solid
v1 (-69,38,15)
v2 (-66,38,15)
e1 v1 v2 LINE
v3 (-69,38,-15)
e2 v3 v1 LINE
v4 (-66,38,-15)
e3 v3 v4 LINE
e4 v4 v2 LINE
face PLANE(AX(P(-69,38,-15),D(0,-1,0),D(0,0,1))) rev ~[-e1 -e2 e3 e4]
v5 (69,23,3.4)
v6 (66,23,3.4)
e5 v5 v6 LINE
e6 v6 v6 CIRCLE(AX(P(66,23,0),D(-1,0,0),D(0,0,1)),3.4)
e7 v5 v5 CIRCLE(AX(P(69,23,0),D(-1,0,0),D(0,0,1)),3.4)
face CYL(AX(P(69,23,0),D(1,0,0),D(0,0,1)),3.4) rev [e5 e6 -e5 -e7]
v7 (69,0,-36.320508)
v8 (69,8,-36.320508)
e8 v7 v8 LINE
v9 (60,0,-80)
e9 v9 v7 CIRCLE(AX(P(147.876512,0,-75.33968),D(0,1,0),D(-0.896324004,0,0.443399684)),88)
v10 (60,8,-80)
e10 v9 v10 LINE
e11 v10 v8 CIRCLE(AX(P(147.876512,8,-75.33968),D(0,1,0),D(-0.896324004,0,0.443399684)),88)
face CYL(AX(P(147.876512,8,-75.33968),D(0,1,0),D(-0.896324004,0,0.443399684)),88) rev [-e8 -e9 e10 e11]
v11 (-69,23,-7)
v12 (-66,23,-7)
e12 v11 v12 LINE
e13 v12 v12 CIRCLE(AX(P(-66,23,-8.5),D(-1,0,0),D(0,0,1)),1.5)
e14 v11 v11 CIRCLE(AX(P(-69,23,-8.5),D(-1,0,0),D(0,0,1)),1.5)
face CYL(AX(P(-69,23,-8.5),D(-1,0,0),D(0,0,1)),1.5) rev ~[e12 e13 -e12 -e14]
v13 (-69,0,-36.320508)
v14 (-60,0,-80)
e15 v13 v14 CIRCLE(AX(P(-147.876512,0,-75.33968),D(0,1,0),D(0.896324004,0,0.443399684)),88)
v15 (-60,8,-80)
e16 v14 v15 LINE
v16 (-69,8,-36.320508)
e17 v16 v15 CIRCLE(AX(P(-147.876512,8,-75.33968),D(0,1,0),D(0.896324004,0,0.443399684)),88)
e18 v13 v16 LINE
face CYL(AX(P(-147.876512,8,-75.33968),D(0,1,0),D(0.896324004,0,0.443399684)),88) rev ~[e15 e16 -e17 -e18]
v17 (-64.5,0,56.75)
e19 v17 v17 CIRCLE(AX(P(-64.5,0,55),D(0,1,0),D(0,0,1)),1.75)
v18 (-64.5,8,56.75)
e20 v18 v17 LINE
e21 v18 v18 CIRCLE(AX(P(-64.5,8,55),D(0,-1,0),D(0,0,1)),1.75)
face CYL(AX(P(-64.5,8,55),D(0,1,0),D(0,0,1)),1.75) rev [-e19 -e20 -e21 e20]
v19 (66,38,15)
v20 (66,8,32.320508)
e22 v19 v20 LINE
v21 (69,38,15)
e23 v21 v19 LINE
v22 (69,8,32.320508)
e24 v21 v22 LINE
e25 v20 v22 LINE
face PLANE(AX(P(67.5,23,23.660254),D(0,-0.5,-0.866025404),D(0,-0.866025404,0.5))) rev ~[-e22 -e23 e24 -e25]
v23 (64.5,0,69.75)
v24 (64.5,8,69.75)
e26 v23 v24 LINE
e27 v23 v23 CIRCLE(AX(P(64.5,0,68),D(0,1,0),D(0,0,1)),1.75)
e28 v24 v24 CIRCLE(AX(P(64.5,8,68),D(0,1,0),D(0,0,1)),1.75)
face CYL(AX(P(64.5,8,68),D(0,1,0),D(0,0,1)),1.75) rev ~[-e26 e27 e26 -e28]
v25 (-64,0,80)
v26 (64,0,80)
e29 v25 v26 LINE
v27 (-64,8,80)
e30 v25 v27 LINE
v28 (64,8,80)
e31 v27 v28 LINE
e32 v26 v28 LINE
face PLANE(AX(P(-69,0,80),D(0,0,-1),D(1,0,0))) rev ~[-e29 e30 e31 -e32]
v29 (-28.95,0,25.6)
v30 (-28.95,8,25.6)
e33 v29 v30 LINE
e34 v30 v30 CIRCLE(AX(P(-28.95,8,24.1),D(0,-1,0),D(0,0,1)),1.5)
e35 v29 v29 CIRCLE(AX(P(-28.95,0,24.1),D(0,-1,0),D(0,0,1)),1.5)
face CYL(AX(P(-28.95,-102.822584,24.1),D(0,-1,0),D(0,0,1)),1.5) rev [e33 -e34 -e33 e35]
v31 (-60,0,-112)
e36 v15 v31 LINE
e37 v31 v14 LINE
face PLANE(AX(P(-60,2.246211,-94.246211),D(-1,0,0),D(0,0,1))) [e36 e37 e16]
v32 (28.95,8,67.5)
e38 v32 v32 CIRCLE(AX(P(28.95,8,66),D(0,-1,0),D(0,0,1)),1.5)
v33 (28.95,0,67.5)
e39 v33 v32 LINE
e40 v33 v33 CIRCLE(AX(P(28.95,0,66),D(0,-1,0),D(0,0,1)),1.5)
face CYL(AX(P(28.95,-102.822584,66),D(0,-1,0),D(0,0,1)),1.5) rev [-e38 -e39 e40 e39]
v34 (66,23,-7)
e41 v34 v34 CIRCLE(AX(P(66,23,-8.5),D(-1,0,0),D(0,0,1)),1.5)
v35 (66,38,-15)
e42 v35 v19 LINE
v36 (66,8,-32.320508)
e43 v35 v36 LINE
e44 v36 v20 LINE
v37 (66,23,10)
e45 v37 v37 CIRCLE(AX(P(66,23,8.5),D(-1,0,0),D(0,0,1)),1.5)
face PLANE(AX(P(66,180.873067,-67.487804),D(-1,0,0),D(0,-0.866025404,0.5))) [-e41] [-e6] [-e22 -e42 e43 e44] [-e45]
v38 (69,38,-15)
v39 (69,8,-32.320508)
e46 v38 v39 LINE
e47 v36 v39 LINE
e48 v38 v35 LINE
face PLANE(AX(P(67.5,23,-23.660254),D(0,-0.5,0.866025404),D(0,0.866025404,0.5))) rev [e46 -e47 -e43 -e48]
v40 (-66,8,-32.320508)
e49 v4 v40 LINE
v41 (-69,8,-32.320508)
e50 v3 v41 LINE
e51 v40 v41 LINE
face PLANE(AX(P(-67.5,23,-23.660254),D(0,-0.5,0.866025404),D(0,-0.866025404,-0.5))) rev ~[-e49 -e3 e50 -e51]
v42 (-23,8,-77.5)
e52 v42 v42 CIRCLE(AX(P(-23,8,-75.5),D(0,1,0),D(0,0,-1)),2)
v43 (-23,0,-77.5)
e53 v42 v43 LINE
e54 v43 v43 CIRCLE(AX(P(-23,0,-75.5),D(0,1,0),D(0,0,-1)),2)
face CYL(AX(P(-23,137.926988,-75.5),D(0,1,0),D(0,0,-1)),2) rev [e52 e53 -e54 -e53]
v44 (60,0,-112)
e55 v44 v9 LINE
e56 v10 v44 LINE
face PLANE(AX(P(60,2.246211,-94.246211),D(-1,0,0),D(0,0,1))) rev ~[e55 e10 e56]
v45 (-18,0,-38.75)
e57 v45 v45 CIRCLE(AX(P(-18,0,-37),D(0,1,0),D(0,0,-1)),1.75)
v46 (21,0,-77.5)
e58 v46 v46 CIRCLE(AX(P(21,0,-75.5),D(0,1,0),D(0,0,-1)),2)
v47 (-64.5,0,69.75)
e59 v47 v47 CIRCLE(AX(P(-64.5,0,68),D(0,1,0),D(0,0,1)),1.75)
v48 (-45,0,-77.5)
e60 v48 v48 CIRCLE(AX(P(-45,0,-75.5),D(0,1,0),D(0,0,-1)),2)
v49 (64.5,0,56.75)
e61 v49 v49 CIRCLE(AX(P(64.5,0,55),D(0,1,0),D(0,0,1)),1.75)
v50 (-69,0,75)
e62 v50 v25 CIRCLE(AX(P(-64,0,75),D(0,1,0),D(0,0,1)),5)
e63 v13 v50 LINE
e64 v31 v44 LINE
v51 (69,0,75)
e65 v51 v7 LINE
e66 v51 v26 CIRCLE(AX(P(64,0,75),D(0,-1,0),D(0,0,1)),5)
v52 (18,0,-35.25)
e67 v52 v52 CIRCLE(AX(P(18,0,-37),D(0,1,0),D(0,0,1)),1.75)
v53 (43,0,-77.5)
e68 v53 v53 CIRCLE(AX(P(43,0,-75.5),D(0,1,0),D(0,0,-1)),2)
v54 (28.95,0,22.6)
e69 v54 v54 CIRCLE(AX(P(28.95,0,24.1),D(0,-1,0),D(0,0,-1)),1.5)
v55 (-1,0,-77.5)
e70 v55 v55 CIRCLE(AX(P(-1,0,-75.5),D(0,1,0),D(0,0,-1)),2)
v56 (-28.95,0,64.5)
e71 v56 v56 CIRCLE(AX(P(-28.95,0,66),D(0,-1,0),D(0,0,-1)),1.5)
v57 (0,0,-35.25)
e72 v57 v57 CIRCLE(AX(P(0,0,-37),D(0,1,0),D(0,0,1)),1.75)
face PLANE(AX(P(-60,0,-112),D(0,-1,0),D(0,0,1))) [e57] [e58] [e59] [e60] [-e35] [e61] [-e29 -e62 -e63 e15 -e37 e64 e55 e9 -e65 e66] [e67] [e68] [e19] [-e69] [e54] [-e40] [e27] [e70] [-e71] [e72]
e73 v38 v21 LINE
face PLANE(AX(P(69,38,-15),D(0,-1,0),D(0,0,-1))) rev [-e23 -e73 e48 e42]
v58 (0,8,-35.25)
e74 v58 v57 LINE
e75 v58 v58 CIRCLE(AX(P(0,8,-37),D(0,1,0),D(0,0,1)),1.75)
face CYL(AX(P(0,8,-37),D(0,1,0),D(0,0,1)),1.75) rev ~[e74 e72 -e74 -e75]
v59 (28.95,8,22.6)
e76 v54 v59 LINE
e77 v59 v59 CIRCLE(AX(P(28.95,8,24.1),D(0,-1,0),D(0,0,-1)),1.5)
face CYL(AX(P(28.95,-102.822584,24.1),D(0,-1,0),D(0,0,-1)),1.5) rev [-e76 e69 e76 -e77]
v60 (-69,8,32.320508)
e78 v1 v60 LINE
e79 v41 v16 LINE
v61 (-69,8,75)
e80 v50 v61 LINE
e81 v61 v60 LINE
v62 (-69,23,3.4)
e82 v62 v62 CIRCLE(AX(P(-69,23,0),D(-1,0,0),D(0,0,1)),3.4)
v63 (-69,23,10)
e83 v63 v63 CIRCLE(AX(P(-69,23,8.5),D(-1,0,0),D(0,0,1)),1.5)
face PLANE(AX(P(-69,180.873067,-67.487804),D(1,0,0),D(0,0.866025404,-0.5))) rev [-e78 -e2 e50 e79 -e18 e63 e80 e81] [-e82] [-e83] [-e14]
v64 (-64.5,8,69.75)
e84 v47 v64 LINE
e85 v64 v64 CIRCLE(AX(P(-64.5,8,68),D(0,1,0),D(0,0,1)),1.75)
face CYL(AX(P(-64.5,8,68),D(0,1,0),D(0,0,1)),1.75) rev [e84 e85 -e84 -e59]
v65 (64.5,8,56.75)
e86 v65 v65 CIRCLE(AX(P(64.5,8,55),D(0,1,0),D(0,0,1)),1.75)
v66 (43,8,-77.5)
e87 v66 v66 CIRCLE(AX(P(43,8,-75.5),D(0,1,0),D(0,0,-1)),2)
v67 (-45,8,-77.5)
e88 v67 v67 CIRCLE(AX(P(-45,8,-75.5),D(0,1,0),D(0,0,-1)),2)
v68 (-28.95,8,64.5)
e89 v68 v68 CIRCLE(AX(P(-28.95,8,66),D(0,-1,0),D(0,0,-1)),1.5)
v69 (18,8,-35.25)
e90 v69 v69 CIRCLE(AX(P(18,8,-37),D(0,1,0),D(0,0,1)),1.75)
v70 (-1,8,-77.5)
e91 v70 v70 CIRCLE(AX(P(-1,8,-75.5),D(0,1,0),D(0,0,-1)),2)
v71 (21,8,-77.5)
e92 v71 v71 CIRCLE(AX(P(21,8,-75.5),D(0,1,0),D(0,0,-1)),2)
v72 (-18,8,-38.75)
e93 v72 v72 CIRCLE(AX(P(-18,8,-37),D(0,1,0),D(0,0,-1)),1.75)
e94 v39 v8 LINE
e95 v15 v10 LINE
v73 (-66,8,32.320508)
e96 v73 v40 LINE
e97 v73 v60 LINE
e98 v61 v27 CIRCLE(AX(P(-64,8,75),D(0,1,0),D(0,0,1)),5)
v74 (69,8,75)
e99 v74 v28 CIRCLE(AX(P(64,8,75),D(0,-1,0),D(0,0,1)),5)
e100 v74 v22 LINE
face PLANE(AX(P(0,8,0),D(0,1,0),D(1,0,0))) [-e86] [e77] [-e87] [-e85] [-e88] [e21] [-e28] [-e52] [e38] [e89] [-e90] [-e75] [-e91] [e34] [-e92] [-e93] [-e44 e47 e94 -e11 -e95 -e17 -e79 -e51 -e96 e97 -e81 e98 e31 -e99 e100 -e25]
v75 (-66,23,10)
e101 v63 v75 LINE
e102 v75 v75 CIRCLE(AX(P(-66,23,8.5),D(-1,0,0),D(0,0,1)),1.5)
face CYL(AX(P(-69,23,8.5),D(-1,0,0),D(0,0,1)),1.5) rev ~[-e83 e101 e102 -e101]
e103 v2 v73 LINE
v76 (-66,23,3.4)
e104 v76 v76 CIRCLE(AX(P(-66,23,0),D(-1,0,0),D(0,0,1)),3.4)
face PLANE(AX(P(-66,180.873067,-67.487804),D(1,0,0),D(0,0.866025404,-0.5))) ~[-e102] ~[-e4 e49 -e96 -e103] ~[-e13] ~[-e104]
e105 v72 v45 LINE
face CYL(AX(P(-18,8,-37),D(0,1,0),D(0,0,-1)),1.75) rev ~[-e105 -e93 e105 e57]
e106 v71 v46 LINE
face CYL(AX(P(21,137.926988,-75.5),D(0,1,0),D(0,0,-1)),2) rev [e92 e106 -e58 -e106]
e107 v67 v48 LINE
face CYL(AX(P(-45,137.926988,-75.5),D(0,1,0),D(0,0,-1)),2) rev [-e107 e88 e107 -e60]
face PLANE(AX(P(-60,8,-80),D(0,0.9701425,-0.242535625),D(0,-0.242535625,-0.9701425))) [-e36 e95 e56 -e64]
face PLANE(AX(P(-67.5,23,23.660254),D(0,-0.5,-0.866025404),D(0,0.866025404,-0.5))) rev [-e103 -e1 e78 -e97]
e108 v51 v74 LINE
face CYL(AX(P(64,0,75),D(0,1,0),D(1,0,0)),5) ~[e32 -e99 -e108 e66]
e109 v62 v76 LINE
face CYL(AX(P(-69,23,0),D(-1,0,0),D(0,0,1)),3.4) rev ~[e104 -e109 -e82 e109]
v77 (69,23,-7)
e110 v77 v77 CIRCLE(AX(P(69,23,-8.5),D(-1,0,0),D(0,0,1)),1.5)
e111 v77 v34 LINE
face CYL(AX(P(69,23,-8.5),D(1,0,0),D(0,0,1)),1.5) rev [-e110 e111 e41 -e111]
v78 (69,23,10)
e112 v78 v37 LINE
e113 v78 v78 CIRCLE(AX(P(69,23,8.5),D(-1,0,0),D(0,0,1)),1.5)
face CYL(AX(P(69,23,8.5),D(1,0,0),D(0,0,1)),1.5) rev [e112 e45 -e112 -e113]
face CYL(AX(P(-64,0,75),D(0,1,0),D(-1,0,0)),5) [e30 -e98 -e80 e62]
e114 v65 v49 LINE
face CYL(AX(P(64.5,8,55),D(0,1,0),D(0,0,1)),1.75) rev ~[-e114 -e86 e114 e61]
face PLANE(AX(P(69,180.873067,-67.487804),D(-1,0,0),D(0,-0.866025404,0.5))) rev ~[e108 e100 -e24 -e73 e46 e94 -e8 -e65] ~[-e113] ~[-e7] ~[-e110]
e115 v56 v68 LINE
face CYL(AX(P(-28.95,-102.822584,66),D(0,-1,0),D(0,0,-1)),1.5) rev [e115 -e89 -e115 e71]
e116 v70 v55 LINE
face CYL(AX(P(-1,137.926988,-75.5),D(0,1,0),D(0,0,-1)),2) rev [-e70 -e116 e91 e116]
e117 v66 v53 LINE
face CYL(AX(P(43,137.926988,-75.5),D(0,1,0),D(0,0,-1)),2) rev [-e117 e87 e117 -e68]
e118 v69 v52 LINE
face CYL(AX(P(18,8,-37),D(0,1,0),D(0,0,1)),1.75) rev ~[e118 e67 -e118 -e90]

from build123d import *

# Parameters (mm, degrees)
SKETCH1_W                = 138
SKETCH1_H                = 160
BOSS_EXTRUDE1_DEPTH      = 8
SKETCH9_W                = 30
SKETCH9_H                = 38
SKETCH9_R                = 3.4
SKETCH9_R_2              = 1.5
BOSS_EXTRUDE4_DEPTH      = 3
RIB2_REACH               = 165.976
SKETCH10_WALL_W          = 364.592232036
SKETCH10_WALL_H          = 3
MIRROR4_COPY_1_REACH     = 165.976
MIRROR4_COPY_1_SKETCH_W  = 364.592232036
MIRROR4_COPY_1_SKETCH_H  = 3
CUT_EXTRUDE2_DEPTH       = 110.822584198
CUT_EXTRUDE2_DEPTH_BACK  = 110.822584198
SKETCH11_R               = 1.5
FILLET1_R                = 5
SKETCH12_R               = 1.75
CUT_EXTRUDE3_DEPTH       = 110.822584198
CUT_EXTRUDE4_DEPTH       = 110.822584198
BOSS_EXTRUDE5_DEPTH      = 60
BOSS_EXTRUDE5_DEPTH_BACK = 60
CUT_EXTRUDE5_DEPTH       = 137.926987844
CUT_EXTRUDE5_DEPTH_BACK  = 137.926987844
SKETCH15_R               = 2
SKETCH16_R               = 1.75
CUT_EXTRUDE6_DEPTH       = 50


with BuildPart() as part:
    # Sketch1 → Boss-Extrude1 (new body)
    with BuildSketch(Plane(origin=(0, 0, 0), x_dir=(1, 0, 0), z_dir=(0, 1, 0))):
        Rectangle(SKETCH1_W, SKETCH1_H)
    extrude(amount=BOSS_EXTRUDE1_DEPTH)

    # Sketch9 → Boss-Extrude4 (add)
    with BuildSketch(Plane.ZY.offset(69)):
        with Locations((0, 19)):
            Rectangle(SKETCH9_W, SKETCH9_H)
        with Locations((0, 23)):
            Circle(SKETCH9_R, mode=Mode.SUBTRACT)
        with Locations((8.5, 23)):
            Circle(SKETCH9_R_2, mode=Mode.SUBTRACT)
        with Locations((-8.5, 23)):
            Circle(SKETCH9_R_2, mode=Mode.SUBTRACT)
    boss_extrude4 = extrude(amount=-BOSS_EXTRUDE4_DEPTH)

    # Sketch10 wall → Rib2 (add, up to next)
    with BuildSketch(Plane(origin=(-69, 23, -23.660254038), x_dir=(0, -0.866025403781, -0.500000000007), z_dir=(0, -0.500000000007, 0.866025403781)), mode=Mode.PRIVATE) as rib2_sk1:
        with Locations((0, 1.5)):
            Rectangle(SKETCH10_WALL_W, SKETCH10_WALL_H)
    rib2_tool1 = extrude(rib2_sk1.sketch, amount=RIB2_REACH, mode=Mode.PRIVATE) - part.part
    rib2 = rib2_tool1.solids().sort_by_distance((-69, 23, -23.660254038))[0]
    add(rib2)

    # Mirror3: Rib2 across plane
    add(rib2.mirror(Plane.XY))

    # Mirror4: Boss-Extrude4, Rib2 across plane
    add(boss_extrude4.mirror(Plane(origin=(0, 0, 0), x_dir=(0, 0, 1), z_dir=(1, 0, 0))))
    add(rib2.mirror(Plane(origin=(0, 0, 0), x_dir=(0, 0, 1), z_dir=(1, 0, 0))))

    # Mirror4 copy 1 sketch → Mirror4 copy 1 (add, up to next)
    with BuildSketch(Plane(origin=(69, 23, 23.660254038), x_dir=(0, -0.866025403781, 0.500000000007), z_dir=(0, -0.500000000007, -0.866025403781)), mode=Mode.PRIVATE) as mirror4_copy_1_sk1:
        with Locations((0, 1.5)):
            Rectangle(MIRROR4_COPY_1_SKETCH_W, MIRROR4_COPY_1_SKETCH_H)
    mirror4_copy_1_tool1 = extrude(mirror4_copy_1_sk1.sketch, amount=MIRROR4_COPY_1_REACH, mode=Mode.PRIVATE) - part.part
    add(mirror4_copy_1_tool1.solids().sort_by_distance((69, 23, 23.660254038))[0])

    # Sketch11 → Cut-Extrude2 (cut, two sides: drawn at the far end of the back side and taken through both)
    with BuildSketch(Plane(origin=(0, 8, 0), x_dir=(1, 0, 0), z_dir=(0, 1, 0)).offset(-CUT_EXTRUDE2_DEPTH_BACK)):
        with Locations(Location((-28.95, -24.1, 0), (0, 0, 270))):
            Circle(SKETCH11_R)
        with Locations(Location((28.95, -24.1, 0), (0, 0, 90))):
            Circle(SKETCH11_R)
        with Locations(Location((-28.95, -66, 0), (0, 0, 90))):
            Circle(SKETCH11_R)
        with Locations(Location((28.95, -66, 0), (0, 0, 270))):
            Circle(SKETCH11_R)
    extrude(amount=CUT_EXTRUDE2_DEPTH + CUT_EXTRUDE2_DEPTH_BACK, mode=Mode.SUBTRACT)

    # Fillet1
    fillet1_edges = [part.edges().sort_by_distance(p)[0] for p in [
        (69, 4, 80),
        (-69, 4, 80),
        (-69, 4, -80),
        (69, 4, -80),
    ]]
    fillet(fillet1_edges, radius=FILLET1_R)

    # Sketch12 → Cut-Extrude3 (cut, symmetric)
    with BuildSketch(Plane(origin=(0, 8, 0), x_dir=(1, 0, 0), z_dir=(0, 1, 0))):
        with Locations(Location((64.5, -55, 0), (0, 0, 270))):
            Circle(SKETCH12_R)
        with Locations(Location((64.5, -68, 0), (0, 0, 270))):
            Circle(SKETCH12_R)
    cut_extrude3 = extrude(amount=CUT_EXTRUDE3_DEPTH, both=True, mode=Mode.SUBTRACT)

    # Mirror5: Cut-Extrude3 across plane
    add(cut_extrude3.mirror(Plane(origin=(0, 0, 0), x_dir=(0, 0, 1), z_dir=(1, 0, 0))), mode=Mode.SUBTRACT)

    # Sketch13 → Cut-Extrude4 (cut, symmetric)
    with BuildSketch(Plane(origin=(0, 8, 0), x_dir=(1, 0, 0), z_dir=(0, 1, 0))):
        with BuildLine():
            Line((60, 80), (80.385419548, 90.585690096))
            Line((80.385419548, 90.585690096), (122.100847158, 60.329129947))
            Line((122.100847158, 60.329129947), (69, 36.320508076))
            ThreePointArc((69, 36.320508076), (61.687085415, 57.580663247), (60, 80))
        make_face()
    cut_extrude4 = extrude(amount=CUT_EXTRUDE4_DEPTH, both=True, mode=Mode.SUBTRACT)

    # Mirror6: Cut-Extrude4 across plane
    add(cut_extrude4.mirror(Plane(origin=(0, 0, 0), x_dir=(0, 0, 1), z_dir=(1, 0, 0))), mode=Mode.SUBTRACT)

    # Sketch14 → Boss-Extrude5 (add, two sides: drawn at the far end of the back side and taken through both)
    with BuildSketch(Plane(origin=(0, 0, 0), x_dir=(0, 0, -1), z_dir=(1, 0, 0)).offset(-BOSS_EXTRUDE5_DEPTH_BACK)):
        Polygon((80, 0), (80, 8), (112, 0), align=None)
    extrude(amount=BOSS_EXTRUDE5_DEPTH + BOSS_EXTRUDE5_DEPTH_BACK)

    # Sketch15 → Cut-Extrude5 (cut, two sides: drawn at the far end of the back side and taken through both)
    with BuildSketch(Plane.XZ.offset(-CUT_EXTRUDE5_DEPTH_BACK)):
        with Locations(Location((-45, -75.5, 0), (0, 0, 270))):
            Circle(SKETCH15_R)
        with Locations(Location((-23, -75.5, 0), (0, 0, 270))):
            Circle(SKETCH15_R)
        with Locations(Location((-1, -75.5, 0), (0, 0, 270))):
            Circle(SKETCH15_R)
        with Locations(Location((21, -75.5, 0), (0, 0, 270))):
            Circle(SKETCH15_R)
        with Locations(Location((43, -75.5, 0), (0, 0, 270))):
            Circle(SKETCH15_R)
    extrude(amount=CUT_EXTRUDE5_DEPTH + CUT_EXTRUDE5_DEPTH_BACK, mode=Mode.SUBTRACT)

    # Sketch16 → Cut-Extrude6 (cut)
    with BuildSketch(Plane(origin=(0, 8, 0), x_dir=(1, 0, 0), z_dir=(0, 1, 0))):
        with Locations(Location((0, 37, 0), (0, 0, 270))):
            Circle(SKETCH16_R)
        with Locations(Location((18, 37, 0), (0, 0, 270))):
            Circle(SKETCH16_R)
        with Locations(Location((-18, 37, 0), (0, 0, 90))):
            Circle(SKETCH16_R)
    extrude(amount=-CUT_EXTRUDE6_DEPTH, mode=Mode.SUBTRACT)


solid = part.part
